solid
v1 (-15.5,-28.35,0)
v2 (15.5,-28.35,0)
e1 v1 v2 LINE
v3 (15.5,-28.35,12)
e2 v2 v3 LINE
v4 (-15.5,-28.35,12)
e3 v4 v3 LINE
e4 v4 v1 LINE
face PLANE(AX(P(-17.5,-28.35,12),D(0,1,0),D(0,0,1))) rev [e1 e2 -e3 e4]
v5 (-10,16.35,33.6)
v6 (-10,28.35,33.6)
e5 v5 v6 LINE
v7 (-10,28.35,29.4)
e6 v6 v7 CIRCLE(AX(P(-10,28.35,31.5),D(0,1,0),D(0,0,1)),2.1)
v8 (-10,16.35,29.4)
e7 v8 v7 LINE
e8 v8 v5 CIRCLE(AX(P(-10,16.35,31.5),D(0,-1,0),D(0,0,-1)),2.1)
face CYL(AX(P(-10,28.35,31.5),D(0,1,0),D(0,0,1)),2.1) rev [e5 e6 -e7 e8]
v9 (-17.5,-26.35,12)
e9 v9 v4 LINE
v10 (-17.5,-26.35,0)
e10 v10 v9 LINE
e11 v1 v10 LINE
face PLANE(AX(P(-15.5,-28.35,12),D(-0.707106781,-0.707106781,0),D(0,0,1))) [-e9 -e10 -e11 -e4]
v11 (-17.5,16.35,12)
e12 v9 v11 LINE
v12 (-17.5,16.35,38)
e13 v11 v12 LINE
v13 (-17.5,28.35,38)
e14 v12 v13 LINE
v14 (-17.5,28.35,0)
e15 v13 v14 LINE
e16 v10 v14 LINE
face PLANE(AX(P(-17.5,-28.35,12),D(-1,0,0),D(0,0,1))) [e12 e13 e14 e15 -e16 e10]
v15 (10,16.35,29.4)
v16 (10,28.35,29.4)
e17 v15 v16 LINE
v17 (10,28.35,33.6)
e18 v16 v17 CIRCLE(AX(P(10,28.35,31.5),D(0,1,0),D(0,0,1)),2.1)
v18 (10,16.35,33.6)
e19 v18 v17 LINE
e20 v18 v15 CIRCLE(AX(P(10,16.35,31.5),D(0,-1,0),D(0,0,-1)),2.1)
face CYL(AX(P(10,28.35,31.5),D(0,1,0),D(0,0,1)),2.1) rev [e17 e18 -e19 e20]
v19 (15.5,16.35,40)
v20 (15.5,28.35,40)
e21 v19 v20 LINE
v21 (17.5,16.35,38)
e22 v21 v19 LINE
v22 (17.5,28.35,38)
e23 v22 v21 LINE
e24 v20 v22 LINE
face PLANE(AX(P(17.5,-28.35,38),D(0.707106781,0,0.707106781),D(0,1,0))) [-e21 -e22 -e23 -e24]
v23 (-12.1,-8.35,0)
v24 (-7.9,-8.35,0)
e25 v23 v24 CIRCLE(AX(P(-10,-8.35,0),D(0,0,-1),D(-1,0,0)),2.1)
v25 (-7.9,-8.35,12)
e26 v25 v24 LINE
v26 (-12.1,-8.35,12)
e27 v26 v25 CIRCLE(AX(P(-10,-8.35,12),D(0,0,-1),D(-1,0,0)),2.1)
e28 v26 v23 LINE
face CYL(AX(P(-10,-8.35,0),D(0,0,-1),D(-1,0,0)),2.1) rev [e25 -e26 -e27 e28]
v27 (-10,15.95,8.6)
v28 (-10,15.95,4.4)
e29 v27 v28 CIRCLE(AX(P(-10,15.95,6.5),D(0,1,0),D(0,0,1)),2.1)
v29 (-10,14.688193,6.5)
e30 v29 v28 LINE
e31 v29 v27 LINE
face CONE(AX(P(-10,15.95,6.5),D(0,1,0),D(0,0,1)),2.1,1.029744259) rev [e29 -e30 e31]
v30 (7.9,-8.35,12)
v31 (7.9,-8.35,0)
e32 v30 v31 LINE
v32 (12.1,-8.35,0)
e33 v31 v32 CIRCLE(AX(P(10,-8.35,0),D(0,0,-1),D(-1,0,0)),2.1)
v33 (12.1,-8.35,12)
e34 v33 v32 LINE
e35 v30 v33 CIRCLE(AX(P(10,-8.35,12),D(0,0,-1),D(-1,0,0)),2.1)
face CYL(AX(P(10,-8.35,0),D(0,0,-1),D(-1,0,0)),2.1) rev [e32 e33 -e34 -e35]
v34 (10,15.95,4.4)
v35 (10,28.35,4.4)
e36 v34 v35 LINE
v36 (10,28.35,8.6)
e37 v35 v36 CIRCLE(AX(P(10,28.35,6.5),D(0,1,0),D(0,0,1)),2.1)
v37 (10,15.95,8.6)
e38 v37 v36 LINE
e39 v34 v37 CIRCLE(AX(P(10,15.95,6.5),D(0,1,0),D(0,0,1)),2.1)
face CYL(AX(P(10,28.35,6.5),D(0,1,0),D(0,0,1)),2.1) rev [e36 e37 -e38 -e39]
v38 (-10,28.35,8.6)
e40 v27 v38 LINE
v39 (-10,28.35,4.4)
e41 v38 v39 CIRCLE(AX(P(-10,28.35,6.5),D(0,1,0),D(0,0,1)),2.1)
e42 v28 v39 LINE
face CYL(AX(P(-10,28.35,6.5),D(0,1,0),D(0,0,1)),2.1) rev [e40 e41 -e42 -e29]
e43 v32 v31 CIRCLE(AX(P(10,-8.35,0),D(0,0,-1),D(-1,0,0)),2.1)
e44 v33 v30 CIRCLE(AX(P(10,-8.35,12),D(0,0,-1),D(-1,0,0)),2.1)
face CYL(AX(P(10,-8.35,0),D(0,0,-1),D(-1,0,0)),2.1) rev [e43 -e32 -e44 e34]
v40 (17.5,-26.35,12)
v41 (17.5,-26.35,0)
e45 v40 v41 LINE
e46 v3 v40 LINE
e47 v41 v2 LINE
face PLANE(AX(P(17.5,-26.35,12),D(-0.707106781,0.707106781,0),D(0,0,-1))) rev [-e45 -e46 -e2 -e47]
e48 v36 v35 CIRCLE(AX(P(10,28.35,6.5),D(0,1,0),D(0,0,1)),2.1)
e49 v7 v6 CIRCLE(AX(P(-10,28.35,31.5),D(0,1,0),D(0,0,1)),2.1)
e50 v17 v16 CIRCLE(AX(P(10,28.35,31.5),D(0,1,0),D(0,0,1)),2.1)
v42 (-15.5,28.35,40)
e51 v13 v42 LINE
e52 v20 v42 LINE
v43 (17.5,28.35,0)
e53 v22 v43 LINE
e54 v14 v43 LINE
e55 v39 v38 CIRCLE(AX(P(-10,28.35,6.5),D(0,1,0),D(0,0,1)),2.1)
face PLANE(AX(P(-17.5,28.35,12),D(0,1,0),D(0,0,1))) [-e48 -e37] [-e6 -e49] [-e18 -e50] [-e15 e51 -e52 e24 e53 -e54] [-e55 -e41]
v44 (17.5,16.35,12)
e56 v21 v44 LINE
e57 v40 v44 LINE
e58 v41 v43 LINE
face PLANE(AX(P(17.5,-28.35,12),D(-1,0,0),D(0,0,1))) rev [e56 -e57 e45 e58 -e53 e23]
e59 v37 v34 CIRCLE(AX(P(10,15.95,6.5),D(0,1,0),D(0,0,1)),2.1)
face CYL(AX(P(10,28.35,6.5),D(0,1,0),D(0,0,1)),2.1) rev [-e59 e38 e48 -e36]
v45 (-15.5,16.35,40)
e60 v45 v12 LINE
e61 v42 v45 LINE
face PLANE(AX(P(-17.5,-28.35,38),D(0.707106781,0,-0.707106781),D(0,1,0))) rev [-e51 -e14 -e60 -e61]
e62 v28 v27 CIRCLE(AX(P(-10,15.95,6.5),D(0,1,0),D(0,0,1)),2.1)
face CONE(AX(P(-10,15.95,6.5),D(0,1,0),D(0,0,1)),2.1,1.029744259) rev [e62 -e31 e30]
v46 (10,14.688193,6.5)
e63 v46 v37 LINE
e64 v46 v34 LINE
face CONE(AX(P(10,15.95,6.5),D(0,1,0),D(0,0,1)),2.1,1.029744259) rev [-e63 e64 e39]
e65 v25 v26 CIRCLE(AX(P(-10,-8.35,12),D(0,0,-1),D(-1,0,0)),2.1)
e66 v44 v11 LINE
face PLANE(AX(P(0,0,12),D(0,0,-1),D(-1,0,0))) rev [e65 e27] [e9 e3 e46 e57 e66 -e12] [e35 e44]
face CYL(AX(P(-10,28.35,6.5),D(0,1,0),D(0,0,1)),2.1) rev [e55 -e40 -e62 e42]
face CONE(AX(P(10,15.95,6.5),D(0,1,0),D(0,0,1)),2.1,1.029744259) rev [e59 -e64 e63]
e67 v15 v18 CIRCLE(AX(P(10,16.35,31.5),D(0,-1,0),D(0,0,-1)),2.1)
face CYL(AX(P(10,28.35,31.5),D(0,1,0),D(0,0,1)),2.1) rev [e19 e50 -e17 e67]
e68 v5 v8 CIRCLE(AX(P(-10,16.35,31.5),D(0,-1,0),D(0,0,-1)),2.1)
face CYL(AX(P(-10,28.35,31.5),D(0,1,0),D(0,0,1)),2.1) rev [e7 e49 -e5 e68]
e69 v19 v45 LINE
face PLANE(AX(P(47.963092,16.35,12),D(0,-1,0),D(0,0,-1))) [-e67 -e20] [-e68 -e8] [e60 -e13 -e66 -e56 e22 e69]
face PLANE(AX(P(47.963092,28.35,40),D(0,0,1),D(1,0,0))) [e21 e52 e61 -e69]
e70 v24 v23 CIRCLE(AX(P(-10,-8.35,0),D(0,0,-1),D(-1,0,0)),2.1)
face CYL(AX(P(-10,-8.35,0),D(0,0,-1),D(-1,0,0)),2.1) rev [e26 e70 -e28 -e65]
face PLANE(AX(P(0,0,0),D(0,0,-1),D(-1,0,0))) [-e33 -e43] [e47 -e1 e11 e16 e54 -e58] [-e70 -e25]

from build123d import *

# Parameters (mm, degrees)
SKETCH_1_W             = 35
SKETCH_1_H             = 56.7
EXTRUDE_1_DEPTH        = 12
CHAMFER_1_SIZE         = 2
SKETCH_4_W             = 28
SKETCH_4_H             = 12
EXTRUDE_2_DEPTH        = 35
HOLE_WIZARD_M5_1_D     = 4.2
CHAMFER_2_SIZE         = 2
HOLE_WIZARD_M5_2_D     = 4.2
HOLE_WIZARD_M5_2_DEPTH = 12.4
HOLE_WIZARD_M5_2_TIP   = 1.2618073


with BuildPart() as part:
    # 草图1 → 凸台-拉伸1 (new body)
    with BuildSketch(Plane.XY):
        Rectangle(SKETCH_1_W, SKETCH_1_H)
    extrude(amount=EXTRUDE_1_DEPTH)

    # 倒角1
    chamfer_1_edges = [part.edges().sort_by_distance(p)[0] for p in [
        (-17.5, -28.35, 6),
        (17.5, -28.35, 6),
    ]]
    chamfer(chamfer_1_edges, length=CHAMFER_1_SIZE)

    # 草图4 → 凸台-拉伸2 (add)
    with BuildSketch(Plane.ZY.offset(17.5)):
        with Locations((26, 22.35)):
            Rectangle(SKETCH_4_W, SKETCH_4_H)
    extrude(amount=-EXTRUDE_2_DEPTH)

    # M5 螺纹孔1 (through all)
    with Locations(Plane(origin=(0, 0, 0), x_dir=(-1, 0, 0), z_dir=(0, 0, -1))):
        with Locations((-10, -8.35), (10, -8.35)):
            Hole(HOLE_WIZARD_M5_1_D / 2)

    # 倒角2
    chamfer_2_edges = [part.edges().sort_by_distance(p)[0] for p in [
        (-17.5, 22.35, 40),
        (17.5, 22.35, 40),
    ]]
    chamfer(chamfer_2_edges, length=CHAMFER_2_SIZE)

    # M5 螺纹孔2
    with Locations(Plane(origin=(0, 28.35, 0), x_dir=(1, 0, 0), z_dir=(0, 1, 0))):
        with Locations((-10, -6.5), (10, -6.5), (-10, -31.5), (10, -31.5)):
            Hole(HOLE_WIZARD_M5_2_D / 2, depth=HOLE_WIZARD_M5_2_DEPTH)
            with Locations((0, 0, -(HOLE_WIZARD_M5_2_DEPTH + HOLE_WIZARD_M5_2_TIP / 2))):  # 118° drill point
                Cone(0, HOLE_WIZARD_M5_2_D / 2, HOLE_WIZARD_M5_2_TIP, mode=Mode.SUBTRACT)


solid = part.part
